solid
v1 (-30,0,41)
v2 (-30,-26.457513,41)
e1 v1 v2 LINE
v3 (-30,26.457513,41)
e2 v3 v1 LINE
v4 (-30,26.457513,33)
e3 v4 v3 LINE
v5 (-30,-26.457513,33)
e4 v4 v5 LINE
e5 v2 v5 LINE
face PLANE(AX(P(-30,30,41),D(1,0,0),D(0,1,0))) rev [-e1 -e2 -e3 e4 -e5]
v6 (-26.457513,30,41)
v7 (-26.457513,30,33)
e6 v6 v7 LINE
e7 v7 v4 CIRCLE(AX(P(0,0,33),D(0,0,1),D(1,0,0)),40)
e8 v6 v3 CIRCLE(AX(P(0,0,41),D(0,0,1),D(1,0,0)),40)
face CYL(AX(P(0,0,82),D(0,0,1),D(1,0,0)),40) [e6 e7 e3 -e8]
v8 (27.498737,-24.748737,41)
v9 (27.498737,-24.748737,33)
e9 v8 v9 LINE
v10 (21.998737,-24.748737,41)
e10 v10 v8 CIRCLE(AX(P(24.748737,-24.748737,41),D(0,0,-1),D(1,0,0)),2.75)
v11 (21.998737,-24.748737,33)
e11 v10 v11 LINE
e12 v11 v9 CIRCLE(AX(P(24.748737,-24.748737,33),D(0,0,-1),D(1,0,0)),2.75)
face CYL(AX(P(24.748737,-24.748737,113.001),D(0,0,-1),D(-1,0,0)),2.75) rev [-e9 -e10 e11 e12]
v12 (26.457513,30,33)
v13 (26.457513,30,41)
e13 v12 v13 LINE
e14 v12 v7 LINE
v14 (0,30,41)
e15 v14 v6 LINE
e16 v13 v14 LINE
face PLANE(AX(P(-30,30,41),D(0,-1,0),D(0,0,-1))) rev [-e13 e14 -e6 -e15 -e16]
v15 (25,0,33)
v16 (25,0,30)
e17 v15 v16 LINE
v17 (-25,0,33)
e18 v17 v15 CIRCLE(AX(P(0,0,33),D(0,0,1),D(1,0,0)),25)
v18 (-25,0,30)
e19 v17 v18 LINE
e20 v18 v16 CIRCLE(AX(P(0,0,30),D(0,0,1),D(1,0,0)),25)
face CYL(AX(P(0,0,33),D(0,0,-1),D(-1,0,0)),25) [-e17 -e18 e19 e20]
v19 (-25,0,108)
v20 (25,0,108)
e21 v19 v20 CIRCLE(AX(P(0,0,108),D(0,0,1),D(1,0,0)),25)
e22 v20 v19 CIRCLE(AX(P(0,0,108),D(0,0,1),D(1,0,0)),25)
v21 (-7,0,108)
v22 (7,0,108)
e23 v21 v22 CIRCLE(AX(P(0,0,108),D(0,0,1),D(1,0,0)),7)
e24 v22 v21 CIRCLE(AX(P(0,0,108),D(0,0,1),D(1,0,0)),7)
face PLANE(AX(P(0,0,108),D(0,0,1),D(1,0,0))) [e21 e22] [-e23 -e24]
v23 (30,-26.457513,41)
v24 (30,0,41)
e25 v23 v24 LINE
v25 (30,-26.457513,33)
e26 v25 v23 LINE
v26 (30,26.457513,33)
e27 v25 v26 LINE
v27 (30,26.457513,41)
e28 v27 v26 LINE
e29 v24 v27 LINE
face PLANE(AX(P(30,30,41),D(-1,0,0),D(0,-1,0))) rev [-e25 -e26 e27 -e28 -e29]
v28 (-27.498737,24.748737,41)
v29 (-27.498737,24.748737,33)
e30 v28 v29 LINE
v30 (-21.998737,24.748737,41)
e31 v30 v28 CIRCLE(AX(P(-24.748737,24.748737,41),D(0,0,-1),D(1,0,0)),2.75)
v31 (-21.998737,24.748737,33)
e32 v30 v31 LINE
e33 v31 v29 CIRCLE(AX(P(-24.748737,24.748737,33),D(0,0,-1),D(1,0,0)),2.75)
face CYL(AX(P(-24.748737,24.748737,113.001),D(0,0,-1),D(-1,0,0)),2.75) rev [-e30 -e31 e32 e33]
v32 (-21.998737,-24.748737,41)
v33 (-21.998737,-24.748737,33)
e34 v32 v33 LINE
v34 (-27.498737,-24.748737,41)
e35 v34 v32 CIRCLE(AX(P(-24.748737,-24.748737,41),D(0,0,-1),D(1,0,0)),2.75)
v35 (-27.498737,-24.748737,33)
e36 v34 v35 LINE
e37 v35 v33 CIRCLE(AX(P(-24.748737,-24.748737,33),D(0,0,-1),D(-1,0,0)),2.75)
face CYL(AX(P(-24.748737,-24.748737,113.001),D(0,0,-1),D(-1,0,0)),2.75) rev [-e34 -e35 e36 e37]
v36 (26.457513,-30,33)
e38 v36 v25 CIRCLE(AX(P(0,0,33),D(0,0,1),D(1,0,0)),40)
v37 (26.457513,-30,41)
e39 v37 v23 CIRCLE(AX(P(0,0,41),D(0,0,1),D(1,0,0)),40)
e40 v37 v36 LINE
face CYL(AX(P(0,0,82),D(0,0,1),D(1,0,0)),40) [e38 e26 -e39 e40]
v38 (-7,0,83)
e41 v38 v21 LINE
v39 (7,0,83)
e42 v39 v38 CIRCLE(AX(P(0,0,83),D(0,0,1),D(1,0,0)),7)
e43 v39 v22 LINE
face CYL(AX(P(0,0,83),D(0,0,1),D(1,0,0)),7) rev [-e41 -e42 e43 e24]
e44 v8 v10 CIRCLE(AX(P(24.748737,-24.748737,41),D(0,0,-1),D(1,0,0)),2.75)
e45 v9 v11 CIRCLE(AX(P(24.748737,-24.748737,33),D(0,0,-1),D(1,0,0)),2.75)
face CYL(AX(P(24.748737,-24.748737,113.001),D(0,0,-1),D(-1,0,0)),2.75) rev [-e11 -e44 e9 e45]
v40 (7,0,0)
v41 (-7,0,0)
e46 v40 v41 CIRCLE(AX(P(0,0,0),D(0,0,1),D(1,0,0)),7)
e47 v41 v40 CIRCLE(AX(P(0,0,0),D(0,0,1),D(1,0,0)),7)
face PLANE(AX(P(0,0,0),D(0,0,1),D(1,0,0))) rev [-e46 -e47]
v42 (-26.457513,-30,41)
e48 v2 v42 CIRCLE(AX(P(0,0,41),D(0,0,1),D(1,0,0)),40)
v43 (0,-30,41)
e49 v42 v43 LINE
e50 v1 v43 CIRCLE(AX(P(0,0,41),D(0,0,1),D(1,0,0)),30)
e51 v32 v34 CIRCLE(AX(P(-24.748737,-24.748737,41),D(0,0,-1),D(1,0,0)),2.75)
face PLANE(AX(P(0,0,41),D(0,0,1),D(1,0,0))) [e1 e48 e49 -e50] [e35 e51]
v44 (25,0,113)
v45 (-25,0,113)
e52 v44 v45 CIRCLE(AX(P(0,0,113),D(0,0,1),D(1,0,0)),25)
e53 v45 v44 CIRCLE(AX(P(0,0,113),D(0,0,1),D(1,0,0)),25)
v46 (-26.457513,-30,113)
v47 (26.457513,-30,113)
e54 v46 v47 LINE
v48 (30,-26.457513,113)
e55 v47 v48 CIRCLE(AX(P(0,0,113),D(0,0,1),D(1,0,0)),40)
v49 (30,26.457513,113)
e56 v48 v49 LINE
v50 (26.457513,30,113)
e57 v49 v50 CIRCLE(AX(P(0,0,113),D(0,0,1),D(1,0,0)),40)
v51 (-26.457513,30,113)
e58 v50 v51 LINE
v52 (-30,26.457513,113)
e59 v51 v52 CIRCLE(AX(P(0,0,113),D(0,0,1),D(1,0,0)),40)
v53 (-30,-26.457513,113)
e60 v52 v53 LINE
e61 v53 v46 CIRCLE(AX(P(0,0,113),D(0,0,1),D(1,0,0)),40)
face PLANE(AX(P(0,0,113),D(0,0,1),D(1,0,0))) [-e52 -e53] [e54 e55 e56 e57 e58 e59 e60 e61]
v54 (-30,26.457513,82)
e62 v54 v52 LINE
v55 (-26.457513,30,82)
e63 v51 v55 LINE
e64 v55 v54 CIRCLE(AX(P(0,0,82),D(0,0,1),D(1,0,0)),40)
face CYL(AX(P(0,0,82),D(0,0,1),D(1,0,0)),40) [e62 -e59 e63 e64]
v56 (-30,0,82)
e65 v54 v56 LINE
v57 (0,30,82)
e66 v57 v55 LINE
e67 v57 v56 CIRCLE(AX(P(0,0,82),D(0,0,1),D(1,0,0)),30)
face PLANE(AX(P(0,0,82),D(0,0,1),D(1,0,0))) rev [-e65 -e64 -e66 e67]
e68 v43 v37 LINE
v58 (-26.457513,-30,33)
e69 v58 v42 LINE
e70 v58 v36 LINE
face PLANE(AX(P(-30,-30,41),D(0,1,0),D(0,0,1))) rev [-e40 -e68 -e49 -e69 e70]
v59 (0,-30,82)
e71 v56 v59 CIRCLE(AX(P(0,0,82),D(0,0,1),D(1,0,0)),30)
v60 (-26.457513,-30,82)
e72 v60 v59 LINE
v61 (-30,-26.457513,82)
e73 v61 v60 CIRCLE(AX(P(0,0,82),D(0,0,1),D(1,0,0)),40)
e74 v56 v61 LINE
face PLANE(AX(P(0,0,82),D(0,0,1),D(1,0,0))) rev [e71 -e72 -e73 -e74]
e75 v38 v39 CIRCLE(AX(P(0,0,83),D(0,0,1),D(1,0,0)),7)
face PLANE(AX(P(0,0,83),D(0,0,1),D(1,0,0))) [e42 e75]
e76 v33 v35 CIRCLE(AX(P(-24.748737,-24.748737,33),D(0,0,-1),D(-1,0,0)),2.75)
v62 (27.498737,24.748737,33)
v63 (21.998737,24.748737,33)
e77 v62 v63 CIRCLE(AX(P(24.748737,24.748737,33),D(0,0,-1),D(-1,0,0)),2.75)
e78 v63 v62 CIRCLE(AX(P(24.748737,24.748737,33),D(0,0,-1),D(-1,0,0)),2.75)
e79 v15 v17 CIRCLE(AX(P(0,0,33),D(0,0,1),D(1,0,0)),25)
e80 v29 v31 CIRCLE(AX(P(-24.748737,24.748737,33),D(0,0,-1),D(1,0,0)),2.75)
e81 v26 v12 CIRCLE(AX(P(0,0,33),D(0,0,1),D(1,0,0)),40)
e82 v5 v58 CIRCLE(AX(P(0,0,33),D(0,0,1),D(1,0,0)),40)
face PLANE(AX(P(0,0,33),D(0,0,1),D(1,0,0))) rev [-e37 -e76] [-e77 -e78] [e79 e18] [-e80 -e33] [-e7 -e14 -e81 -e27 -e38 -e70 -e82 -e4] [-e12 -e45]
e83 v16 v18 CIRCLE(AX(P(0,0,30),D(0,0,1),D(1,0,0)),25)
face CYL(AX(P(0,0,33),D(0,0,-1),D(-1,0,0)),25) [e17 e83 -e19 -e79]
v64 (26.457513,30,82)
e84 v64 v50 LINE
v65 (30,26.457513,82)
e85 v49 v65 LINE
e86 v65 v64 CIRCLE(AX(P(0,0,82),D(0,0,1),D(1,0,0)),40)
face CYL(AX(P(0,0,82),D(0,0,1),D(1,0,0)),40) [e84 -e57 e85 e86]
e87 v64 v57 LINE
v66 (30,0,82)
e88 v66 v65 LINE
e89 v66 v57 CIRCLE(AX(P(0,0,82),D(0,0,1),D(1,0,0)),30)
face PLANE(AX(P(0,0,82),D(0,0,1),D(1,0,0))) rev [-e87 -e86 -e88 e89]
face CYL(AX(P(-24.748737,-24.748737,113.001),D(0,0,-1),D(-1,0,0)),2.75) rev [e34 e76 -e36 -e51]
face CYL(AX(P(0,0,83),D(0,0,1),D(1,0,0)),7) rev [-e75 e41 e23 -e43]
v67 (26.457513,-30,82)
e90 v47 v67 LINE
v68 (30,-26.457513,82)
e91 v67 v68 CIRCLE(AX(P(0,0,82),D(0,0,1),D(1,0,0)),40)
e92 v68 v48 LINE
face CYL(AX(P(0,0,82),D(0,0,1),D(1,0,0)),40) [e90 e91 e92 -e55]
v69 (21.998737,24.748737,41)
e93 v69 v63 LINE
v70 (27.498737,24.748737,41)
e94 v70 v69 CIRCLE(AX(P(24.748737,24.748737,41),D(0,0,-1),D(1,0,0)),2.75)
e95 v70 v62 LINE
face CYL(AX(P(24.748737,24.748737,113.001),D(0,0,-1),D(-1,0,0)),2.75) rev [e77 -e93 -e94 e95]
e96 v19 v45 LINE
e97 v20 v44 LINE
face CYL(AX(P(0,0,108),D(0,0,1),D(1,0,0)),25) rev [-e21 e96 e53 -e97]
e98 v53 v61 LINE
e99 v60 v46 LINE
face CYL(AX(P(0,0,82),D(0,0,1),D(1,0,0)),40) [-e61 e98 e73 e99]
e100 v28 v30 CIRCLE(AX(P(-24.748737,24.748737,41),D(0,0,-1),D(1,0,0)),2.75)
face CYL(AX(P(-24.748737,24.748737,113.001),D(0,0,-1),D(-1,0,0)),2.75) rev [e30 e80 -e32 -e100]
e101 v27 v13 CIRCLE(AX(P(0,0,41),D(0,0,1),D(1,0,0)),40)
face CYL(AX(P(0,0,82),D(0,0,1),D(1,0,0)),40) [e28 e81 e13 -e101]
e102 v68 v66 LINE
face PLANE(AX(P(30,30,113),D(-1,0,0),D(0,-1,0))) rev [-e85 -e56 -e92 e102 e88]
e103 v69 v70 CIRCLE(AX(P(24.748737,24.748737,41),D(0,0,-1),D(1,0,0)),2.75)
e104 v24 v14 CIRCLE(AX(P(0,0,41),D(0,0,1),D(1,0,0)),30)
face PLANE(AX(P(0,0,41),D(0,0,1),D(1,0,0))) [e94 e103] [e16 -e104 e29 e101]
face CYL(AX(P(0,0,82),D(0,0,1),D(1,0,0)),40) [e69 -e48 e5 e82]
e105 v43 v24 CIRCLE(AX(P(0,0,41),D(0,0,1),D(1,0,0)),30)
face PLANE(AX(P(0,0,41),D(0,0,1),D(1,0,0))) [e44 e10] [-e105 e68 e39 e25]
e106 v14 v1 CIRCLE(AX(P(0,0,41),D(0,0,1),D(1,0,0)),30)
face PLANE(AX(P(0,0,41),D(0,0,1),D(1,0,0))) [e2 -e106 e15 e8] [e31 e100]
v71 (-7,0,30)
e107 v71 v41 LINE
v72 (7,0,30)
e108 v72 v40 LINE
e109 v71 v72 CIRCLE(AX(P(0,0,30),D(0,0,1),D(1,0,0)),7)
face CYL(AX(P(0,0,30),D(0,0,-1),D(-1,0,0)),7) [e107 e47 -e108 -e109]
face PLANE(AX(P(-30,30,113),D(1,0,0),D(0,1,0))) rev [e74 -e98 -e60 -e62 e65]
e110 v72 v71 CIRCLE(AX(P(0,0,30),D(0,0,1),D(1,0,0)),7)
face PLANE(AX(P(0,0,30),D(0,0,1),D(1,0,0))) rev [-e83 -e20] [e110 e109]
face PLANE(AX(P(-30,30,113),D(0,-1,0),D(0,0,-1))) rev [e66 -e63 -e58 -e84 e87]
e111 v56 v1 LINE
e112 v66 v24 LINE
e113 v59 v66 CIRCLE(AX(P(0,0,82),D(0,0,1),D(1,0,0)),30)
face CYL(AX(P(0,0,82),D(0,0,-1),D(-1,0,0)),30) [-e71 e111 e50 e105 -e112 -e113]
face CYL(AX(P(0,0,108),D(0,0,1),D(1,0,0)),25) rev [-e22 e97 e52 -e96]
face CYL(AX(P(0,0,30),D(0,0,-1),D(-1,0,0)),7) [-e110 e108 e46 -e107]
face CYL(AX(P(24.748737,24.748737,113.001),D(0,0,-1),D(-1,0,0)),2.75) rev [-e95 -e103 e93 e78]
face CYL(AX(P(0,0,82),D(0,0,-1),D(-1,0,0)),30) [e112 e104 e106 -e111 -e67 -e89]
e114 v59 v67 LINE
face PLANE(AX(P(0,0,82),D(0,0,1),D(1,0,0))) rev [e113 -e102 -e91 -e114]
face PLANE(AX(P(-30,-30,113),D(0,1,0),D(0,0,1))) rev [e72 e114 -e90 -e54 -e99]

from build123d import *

# Parameters (mm, degrees)
SKETCH_1_R          = 7
EXTRUDE_1_DEPTH     = 30
SKETCH_2_R          = 25
EXTRUDE_2_DEPTH     = 3
SKETCH_3_W          = 60
SKETCH_3_H          = 60
EXTRUDE_3_DEPTH     = 8
SKETCH_4_R          = 30
EXTRUDE_4_DEPTH     = 41
SKETCH_5_W          = 60
SKETCH_5_H          = 60
EXTRUDE_5_DEPTH     = 31
SKETCH_6_W          = 7.340334956
SKETCH_6_H          = 80
CUT_EXTRUDE_1_REACH = 92.554
SKETCH_7_R          = 2.75
CUT_EXTRUDE_START   = -5
SKETCH_8_R          = 25
CUT_EXTRUDE_2_DEPTH = 5
CUT_EXTRUDE_START_2 = -25
SKETCH_9_R          = 7
CUT_EXTRUDE_3_DEPTH = 25


with BuildPart() as part:
    # 草图1 → 凸台-拉伸1 (new body)
    with BuildSketch(Plane.XY):
        Circle(SKETCH_1_R)
    extrude(amount=EXTRUDE_1_DEPTH)

    # 草图2 → 凸台-拉伸2 (add)
    with BuildSketch(Plane.XY.offset(30)):
        Circle(SKETCH_2_R)
    extrude(amount=EXTRUDE_2_DEPTH)

    # 草图3 → 凸台-拉伸3 (add)
    with BuildSketch(Plane.XY.offset(33)):
        Rectangle(SKETCH_3_W, SKETCH_3_H)
    extrude(amount=EXTRUDE_3_DEPTH)

    # 草图4 → 凸台-拉伸4 (add)
    with BuildSketch(Plane.XY.offset(41)):
        Circle(SKETCH_4_R)
    extrude(amount=EXTRUDE_4_DEPTH)

    # 草图5 → 凸台-拉伸5 (add)
    with BuildSketch(Plane.XY.offset(82)):
        Rectangle(SKETCH_5_W, SKETCH_5_H)
    extrude(amount=EXTRUDE_5_DEPTH)

    # 草图6 → 切除-旋转1 (revolve, cut)
    with BuildSketch(Plane(origin=(0, 0, 0), x_dir=(1, 0, 0), z_dir=(0, 1, 0))):
        with Locations((-43.670167478, -73)):
            Rectangle(SKETCH_6_W, SKETCH_6_H)
    revolve(axis=Axis((0, 0, 82), (0, 0, -1)), mode=Mode.SUBTRACT)

    # 草图7 → 切除-拉伸1 (cut, up to next)
    with BuildSketch(Plane(origin=(0, 0, 33), x_dir=(-1, 0, 0), z_dir=(0, 0, -1)), mode=Mode.PRIVATE) as cut_extrude_1_sk1:
        with Locations((-24.748737342, 24.748737342)):
            Circle(SKETCH_7_R)
    cut_extrude_1_tool1 = extrude(cut_extrude_1_sk1.sketch, amount=-CUT_EXTRUDE_1_REACH, mode=Mode.PRIVATE) & part.part
    # 草图7 → 切除-拉伸1 (cut, up to next)
    with BuildSketch(Plane(origin=(0, 0, 33), x_dir=(-1, 0, 0), z_dir=(0, 0, -1)), mode=Mode.PRIVATE) as cut_extrude_1_sk2:
        with Locations(Location((24.748737342, 24.748737342, 0), (0, 0, 180))):
            Circle(SKETCH_7_R)
    cut_extrude_1_tool2 = extrude(cut_extrude_1_sk2.sketch, amount=-CUT_EXTRUDE_1_REACH, mode=Mode.PRIVATE) & part.part
    # 草图7 → 切除-拉伸1 (cut, up to next)
    with BuildSketch(Plane(origin=(0, 0, 33), x_dir=(-1, 0, 0), z_dir=(0, 0, -1)), mode=Mode.PRIVATE) as cut_extrude_1_sk3:
        with Locations(Location((-24.748737342, -24.748737342, 0), (0, 0, 180))):
            Circle(SKETCH_7_R)
    cut_extrude_1_tool3 = extrude(cut_extrude_1_sk3.sketch, amount=-CUT_EXTRUDE_1_REACH, mode=Mode.PRIVATE) & part.part
    # 草图7 → 切除-拉伸1 (cut, up to next)
    with BuildSketch(Plane(origin=(0, 0, 33), x_dir=(-1, 0, 0), z_dir=(0, 0, -1)), mode=Mode.PRIVATE) as cut_extrude_1_sk4:
        with Locations((24.748737342, -24.748737342)):
            Circle(SKETCH_7_R)
    cut_extrude_1_tool4 = extrude(cut_extrude_1_sk4.sketch, amount=-CUT_EXTRUDE_1_REACH, mode=Mode.PRIVATE) & part.part
    add(cut_extrude_1_tool1.solids().sort_by_distance((24.748737, 24.748737, 33))[0], mode=Mode.SUBTRACT)
    add(cut_extrude_1_tool2.solids().sort_by_distance((-24.748737, 24.748737, 33))[0], mode=Mode.SUBTRACT)
    add(cut_extrude_1_tool3.solids().sort_by_distance((24.748737, -24.748737, 33))[0], mode=Mode.SUBTRACT)
    add(cut_extrude_1_tool4.solids().sort_by_distance((-24.748737, -24.748737, 33))[0], mode=Mode.SUBTRACT)

    # 草图8 → 切除-拉伸2 (cut)
    with BuildSketch(Plane.XY.offset(113).offset(CUT_EXTRUDE_START)):
        Circle(SKETCH_8_R)
    extrude(amount=CUT_EXTRUDE_2_DEPTH, mode=Mode.SUBTRACT)

    # 草图9 → 切除-拉伸3 (cut)
    with BuildSketch(Plane.XY.offset(108).offset(CUT_EXTRUDE_START_2)):
        Circle(SKETCH_9_R)
    extrude(amount=CUT_EXTRUDE_3_DEPTH, mode=Mode.SUBTRACT)


solid = part.part
